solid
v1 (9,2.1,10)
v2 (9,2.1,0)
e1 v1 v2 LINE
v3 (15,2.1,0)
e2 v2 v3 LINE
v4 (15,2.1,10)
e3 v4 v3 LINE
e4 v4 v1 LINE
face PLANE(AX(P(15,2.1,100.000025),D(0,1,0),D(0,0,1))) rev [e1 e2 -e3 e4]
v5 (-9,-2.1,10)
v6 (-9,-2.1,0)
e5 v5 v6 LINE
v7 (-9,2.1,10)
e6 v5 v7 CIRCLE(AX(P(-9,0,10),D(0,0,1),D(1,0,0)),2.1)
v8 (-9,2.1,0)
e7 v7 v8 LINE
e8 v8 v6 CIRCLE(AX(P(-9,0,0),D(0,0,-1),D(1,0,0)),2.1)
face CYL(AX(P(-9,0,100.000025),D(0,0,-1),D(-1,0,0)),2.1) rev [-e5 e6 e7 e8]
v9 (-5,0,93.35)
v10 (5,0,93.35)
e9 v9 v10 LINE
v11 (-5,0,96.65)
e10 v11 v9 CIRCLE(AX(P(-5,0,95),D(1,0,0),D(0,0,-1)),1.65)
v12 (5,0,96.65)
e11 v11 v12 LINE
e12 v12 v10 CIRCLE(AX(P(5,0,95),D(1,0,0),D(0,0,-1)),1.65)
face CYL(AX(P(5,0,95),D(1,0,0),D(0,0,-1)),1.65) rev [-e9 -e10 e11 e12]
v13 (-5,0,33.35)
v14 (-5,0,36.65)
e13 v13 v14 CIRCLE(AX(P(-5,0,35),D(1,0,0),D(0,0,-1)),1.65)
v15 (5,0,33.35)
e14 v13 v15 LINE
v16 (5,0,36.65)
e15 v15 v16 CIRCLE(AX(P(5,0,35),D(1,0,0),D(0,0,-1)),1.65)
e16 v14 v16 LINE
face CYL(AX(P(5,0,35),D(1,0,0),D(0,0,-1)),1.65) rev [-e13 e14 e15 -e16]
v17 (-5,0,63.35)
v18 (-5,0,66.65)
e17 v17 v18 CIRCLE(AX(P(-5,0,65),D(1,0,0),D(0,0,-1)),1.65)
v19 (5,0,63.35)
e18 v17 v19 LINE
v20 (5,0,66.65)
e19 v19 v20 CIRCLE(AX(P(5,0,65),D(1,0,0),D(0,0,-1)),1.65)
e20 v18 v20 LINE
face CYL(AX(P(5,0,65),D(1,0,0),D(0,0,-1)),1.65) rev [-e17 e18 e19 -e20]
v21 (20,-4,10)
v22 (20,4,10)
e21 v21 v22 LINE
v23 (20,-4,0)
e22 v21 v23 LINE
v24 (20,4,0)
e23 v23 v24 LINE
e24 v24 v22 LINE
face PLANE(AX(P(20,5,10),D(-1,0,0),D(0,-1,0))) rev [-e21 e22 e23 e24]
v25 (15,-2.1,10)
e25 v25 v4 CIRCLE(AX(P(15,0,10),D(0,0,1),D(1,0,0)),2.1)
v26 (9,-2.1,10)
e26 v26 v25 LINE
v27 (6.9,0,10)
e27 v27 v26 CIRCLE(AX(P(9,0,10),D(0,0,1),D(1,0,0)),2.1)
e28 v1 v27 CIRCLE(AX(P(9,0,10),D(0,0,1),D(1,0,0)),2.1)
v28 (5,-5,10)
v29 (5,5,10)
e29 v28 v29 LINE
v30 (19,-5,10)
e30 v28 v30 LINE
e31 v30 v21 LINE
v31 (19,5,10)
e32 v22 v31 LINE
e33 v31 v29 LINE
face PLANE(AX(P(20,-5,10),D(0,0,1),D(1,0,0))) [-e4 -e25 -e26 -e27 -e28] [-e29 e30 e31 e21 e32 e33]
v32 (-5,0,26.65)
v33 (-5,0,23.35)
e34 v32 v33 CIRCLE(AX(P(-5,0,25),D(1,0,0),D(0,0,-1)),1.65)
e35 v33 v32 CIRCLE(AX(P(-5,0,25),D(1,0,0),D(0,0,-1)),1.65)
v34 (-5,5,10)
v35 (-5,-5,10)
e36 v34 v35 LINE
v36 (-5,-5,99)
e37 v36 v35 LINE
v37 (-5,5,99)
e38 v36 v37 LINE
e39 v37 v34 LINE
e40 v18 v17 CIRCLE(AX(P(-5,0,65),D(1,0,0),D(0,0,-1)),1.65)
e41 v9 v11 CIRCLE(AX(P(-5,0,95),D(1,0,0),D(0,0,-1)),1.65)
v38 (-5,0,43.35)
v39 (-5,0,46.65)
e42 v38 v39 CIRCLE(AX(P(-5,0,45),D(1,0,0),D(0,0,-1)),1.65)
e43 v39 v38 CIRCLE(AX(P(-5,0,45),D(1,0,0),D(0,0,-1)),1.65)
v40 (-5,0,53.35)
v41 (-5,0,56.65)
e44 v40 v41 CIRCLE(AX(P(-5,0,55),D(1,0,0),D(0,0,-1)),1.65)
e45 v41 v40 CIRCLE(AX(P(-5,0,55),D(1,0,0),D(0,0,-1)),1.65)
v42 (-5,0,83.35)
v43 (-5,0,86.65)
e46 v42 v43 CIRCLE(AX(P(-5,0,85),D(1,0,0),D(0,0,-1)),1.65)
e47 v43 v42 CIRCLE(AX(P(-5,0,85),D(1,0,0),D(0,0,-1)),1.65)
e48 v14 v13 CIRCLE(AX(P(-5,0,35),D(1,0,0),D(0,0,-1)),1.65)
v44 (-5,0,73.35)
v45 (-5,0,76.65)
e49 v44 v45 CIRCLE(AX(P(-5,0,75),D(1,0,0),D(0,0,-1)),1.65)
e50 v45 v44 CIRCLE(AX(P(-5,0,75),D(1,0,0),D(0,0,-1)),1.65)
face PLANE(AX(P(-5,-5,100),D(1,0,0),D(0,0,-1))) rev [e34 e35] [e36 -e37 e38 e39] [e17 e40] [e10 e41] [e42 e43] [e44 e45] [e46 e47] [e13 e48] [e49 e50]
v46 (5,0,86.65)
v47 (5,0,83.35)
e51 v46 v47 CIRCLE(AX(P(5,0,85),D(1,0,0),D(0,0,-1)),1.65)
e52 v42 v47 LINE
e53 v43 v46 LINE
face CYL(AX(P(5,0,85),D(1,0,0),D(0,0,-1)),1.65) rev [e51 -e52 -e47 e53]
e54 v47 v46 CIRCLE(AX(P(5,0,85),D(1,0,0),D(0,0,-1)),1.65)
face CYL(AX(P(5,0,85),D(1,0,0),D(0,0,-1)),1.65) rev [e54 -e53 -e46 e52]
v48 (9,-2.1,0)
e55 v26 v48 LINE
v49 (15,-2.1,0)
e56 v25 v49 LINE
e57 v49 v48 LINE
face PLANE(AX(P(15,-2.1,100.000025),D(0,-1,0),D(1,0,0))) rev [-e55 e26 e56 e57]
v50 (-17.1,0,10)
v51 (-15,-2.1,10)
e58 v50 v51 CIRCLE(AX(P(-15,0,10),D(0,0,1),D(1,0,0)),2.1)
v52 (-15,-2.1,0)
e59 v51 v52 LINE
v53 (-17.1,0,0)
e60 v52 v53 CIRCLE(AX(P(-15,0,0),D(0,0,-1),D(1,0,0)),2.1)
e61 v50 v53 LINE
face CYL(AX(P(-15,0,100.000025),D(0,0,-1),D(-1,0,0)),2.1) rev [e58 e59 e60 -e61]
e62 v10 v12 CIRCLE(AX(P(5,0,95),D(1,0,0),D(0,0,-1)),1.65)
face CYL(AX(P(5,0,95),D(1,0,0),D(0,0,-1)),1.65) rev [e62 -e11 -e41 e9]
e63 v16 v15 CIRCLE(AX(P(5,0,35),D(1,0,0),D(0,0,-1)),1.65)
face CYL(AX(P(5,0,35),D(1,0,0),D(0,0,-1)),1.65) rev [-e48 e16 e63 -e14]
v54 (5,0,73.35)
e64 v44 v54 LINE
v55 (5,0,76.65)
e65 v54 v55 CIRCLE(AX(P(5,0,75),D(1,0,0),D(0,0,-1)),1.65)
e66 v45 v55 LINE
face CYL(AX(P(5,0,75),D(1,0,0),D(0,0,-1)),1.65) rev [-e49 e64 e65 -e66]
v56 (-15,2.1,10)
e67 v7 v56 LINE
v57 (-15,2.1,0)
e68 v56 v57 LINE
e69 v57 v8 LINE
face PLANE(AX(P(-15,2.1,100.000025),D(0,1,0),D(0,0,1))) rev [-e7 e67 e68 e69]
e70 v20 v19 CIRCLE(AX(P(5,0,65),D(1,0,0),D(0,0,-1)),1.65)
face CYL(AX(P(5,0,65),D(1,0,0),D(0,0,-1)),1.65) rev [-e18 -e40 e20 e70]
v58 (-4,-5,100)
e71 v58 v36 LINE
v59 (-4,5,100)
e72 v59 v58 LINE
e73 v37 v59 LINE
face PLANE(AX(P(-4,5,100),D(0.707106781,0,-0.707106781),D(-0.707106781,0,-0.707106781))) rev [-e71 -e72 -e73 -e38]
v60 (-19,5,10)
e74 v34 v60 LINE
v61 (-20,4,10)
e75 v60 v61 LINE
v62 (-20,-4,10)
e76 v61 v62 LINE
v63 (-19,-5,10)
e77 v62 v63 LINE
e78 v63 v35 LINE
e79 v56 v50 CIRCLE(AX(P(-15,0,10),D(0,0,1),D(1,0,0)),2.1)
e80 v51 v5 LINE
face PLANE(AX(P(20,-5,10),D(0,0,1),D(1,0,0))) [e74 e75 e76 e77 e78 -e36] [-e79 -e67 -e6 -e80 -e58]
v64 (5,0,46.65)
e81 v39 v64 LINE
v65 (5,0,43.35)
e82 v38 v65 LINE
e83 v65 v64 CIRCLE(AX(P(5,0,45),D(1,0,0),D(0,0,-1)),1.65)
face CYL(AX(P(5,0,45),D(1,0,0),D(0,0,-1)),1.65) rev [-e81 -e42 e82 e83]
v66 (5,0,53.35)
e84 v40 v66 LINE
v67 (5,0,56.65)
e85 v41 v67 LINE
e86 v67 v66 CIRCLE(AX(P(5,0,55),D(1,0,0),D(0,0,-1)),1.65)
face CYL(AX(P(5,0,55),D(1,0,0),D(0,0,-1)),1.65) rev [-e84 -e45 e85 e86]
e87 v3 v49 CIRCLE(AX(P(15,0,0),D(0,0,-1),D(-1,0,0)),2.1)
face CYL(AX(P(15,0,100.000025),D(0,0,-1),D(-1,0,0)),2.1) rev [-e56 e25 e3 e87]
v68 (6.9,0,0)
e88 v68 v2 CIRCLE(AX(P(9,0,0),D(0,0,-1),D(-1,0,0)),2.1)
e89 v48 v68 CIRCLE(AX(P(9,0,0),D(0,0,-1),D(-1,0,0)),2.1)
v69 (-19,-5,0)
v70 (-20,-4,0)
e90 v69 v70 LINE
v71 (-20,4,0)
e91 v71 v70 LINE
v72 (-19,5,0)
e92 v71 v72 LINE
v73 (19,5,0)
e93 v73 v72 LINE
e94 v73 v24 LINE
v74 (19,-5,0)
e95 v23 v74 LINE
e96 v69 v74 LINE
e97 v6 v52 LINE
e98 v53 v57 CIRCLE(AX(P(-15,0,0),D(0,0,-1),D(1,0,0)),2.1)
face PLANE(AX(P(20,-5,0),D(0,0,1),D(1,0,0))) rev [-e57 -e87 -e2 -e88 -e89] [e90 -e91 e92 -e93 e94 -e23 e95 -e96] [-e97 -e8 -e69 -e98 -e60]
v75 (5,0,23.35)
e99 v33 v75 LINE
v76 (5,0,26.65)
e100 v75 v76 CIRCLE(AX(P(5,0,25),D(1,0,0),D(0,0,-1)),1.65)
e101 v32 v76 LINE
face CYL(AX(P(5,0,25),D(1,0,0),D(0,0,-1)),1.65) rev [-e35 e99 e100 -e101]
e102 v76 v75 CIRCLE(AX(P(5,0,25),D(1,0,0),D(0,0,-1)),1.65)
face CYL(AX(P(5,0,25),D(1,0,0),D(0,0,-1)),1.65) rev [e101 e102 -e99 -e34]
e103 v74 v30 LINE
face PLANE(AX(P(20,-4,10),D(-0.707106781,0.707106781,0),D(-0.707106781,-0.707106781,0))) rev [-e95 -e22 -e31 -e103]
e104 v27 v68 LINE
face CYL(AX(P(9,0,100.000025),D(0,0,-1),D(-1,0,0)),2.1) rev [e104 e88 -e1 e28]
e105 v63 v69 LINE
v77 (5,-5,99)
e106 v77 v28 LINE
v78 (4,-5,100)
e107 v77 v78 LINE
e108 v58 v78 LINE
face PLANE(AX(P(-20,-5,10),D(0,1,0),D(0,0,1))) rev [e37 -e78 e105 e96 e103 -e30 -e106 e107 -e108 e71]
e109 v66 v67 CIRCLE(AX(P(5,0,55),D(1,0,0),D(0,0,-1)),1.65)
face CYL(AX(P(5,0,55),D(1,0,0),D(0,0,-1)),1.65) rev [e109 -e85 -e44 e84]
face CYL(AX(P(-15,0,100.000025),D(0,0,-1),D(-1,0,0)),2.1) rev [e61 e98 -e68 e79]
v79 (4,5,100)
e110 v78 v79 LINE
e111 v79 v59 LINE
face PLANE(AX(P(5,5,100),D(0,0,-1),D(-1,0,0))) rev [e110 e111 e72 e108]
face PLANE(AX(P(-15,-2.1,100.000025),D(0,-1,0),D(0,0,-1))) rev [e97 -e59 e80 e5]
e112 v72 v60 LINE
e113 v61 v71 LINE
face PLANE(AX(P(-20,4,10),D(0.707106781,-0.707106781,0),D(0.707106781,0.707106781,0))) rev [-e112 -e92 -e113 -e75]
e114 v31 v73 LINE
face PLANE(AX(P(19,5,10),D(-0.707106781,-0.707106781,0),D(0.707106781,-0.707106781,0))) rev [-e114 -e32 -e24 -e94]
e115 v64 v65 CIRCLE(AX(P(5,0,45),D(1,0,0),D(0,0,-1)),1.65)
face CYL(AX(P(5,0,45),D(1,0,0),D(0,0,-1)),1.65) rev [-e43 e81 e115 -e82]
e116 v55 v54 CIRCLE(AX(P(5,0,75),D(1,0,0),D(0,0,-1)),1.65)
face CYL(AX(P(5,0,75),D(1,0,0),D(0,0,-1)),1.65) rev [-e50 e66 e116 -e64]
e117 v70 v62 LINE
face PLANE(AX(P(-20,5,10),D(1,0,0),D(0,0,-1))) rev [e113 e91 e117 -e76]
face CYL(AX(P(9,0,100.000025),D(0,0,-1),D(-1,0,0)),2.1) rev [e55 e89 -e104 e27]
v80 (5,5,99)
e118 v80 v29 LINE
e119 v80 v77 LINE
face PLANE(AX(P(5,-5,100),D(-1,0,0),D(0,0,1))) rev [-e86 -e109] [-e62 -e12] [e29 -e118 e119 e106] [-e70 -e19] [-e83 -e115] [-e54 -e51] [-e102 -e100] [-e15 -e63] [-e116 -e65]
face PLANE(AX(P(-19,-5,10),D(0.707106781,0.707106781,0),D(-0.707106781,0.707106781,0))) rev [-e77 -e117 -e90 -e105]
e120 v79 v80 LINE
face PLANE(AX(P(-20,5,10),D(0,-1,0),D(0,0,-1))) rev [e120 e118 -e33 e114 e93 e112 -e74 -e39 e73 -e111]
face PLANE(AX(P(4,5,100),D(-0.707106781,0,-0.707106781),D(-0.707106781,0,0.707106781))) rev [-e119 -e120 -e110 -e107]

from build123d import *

# Parameters (mm, degrees)
SKETCH1_W           = 40
SKETCH1_H           = 10
BOSS_EXTRUDE1_DEPTH = 10
SKETCH2_W           = 10
SKETCH2_H           = 10
BOSS_EXTRUDE2_DEPTH = 90
CUT_EXTRUDE1_DEPTH  = 103.102889283
M4_TAPPED_HOLE1_D   = 3.3
CHAMFER1_SIZE       = 1


with BuildPart() as part:
    # Sketch1 → Boss-Extrude1 (new body)
    with BuildSketch(Plane.XY):
        Rectangle(SKETCH1_W, SKETCH1_H)
    extrude(amount=BOSS_EXTRUDE1_DEPTH)

    # Sketch2 → Boss-Extrude2 (add)
    with BuildSketch(Plane.XY.offset(10)):
        Rectangle(SKETCH2_W, SKETCH2_H)
    extrude(amount=BOSS_EXTRUDE2_DEPTH)

    # Sketch3 → Cut-Extrude1 (cut, through all)
    with BuildSketch(Plane(origin=(0, 0, 0), x_dir=(-1, 0, 0), z_dir=(0, 0, -1))):
        with BuildLine():
            Line((-15, 2.1), (-9, 2.1))
            ThreePointArc((-9, 2.1), (-6.9, 0), (-9, -2.1))
            Line((-9, -2.1), (-15, -2.1))
            ThreePointArc((-15, -2.1), (-17.1, 0), (-15, 2.1))
        make_face()
        with BuildLine():
            Line((15, 2.1), (9, 2.1))
            ThreePointArc((9, 2.1), (6.9, 0), (9, -2.1))
            Line((9, -2.1), (15, -2.1))
            ThreePointArc((15, -2.1), (17.1, 0), (15, 2.1))
        make_face()
    extrude(amount=-CUT_EXTRUDE1_DEPTH, mode=Mode.SUBTRACT)

    # M4 Tapped Hole1 (through all)
    with Locations(Plane(origin=(5, 0, 0), x_dir=(0, 0, -1), z_dir=(1, 0, 0))):
        with Locations((-25, 0), (-35, 0), (-45, 0), (-55, 0), (-65, 0), (-75, 0), (-85, 0), (-95, 0)):
            Hole(M4_TAPPED_HOLE1_D / 2)

    # Chamfer1
    chamfer1_edges = [part.edges().sort_by_distance(p)[0] for p in [
        (20, 5, 5),
        (20, -5, 5),
        (-20, -5, 5),
        (-20, 5, 5),
        (5, 0, 100),
        (-5, 0, 100),
    ]]
    chamfer(chamfer1_edges, length=CHAMFER1_SIZE)


solid = part.part
